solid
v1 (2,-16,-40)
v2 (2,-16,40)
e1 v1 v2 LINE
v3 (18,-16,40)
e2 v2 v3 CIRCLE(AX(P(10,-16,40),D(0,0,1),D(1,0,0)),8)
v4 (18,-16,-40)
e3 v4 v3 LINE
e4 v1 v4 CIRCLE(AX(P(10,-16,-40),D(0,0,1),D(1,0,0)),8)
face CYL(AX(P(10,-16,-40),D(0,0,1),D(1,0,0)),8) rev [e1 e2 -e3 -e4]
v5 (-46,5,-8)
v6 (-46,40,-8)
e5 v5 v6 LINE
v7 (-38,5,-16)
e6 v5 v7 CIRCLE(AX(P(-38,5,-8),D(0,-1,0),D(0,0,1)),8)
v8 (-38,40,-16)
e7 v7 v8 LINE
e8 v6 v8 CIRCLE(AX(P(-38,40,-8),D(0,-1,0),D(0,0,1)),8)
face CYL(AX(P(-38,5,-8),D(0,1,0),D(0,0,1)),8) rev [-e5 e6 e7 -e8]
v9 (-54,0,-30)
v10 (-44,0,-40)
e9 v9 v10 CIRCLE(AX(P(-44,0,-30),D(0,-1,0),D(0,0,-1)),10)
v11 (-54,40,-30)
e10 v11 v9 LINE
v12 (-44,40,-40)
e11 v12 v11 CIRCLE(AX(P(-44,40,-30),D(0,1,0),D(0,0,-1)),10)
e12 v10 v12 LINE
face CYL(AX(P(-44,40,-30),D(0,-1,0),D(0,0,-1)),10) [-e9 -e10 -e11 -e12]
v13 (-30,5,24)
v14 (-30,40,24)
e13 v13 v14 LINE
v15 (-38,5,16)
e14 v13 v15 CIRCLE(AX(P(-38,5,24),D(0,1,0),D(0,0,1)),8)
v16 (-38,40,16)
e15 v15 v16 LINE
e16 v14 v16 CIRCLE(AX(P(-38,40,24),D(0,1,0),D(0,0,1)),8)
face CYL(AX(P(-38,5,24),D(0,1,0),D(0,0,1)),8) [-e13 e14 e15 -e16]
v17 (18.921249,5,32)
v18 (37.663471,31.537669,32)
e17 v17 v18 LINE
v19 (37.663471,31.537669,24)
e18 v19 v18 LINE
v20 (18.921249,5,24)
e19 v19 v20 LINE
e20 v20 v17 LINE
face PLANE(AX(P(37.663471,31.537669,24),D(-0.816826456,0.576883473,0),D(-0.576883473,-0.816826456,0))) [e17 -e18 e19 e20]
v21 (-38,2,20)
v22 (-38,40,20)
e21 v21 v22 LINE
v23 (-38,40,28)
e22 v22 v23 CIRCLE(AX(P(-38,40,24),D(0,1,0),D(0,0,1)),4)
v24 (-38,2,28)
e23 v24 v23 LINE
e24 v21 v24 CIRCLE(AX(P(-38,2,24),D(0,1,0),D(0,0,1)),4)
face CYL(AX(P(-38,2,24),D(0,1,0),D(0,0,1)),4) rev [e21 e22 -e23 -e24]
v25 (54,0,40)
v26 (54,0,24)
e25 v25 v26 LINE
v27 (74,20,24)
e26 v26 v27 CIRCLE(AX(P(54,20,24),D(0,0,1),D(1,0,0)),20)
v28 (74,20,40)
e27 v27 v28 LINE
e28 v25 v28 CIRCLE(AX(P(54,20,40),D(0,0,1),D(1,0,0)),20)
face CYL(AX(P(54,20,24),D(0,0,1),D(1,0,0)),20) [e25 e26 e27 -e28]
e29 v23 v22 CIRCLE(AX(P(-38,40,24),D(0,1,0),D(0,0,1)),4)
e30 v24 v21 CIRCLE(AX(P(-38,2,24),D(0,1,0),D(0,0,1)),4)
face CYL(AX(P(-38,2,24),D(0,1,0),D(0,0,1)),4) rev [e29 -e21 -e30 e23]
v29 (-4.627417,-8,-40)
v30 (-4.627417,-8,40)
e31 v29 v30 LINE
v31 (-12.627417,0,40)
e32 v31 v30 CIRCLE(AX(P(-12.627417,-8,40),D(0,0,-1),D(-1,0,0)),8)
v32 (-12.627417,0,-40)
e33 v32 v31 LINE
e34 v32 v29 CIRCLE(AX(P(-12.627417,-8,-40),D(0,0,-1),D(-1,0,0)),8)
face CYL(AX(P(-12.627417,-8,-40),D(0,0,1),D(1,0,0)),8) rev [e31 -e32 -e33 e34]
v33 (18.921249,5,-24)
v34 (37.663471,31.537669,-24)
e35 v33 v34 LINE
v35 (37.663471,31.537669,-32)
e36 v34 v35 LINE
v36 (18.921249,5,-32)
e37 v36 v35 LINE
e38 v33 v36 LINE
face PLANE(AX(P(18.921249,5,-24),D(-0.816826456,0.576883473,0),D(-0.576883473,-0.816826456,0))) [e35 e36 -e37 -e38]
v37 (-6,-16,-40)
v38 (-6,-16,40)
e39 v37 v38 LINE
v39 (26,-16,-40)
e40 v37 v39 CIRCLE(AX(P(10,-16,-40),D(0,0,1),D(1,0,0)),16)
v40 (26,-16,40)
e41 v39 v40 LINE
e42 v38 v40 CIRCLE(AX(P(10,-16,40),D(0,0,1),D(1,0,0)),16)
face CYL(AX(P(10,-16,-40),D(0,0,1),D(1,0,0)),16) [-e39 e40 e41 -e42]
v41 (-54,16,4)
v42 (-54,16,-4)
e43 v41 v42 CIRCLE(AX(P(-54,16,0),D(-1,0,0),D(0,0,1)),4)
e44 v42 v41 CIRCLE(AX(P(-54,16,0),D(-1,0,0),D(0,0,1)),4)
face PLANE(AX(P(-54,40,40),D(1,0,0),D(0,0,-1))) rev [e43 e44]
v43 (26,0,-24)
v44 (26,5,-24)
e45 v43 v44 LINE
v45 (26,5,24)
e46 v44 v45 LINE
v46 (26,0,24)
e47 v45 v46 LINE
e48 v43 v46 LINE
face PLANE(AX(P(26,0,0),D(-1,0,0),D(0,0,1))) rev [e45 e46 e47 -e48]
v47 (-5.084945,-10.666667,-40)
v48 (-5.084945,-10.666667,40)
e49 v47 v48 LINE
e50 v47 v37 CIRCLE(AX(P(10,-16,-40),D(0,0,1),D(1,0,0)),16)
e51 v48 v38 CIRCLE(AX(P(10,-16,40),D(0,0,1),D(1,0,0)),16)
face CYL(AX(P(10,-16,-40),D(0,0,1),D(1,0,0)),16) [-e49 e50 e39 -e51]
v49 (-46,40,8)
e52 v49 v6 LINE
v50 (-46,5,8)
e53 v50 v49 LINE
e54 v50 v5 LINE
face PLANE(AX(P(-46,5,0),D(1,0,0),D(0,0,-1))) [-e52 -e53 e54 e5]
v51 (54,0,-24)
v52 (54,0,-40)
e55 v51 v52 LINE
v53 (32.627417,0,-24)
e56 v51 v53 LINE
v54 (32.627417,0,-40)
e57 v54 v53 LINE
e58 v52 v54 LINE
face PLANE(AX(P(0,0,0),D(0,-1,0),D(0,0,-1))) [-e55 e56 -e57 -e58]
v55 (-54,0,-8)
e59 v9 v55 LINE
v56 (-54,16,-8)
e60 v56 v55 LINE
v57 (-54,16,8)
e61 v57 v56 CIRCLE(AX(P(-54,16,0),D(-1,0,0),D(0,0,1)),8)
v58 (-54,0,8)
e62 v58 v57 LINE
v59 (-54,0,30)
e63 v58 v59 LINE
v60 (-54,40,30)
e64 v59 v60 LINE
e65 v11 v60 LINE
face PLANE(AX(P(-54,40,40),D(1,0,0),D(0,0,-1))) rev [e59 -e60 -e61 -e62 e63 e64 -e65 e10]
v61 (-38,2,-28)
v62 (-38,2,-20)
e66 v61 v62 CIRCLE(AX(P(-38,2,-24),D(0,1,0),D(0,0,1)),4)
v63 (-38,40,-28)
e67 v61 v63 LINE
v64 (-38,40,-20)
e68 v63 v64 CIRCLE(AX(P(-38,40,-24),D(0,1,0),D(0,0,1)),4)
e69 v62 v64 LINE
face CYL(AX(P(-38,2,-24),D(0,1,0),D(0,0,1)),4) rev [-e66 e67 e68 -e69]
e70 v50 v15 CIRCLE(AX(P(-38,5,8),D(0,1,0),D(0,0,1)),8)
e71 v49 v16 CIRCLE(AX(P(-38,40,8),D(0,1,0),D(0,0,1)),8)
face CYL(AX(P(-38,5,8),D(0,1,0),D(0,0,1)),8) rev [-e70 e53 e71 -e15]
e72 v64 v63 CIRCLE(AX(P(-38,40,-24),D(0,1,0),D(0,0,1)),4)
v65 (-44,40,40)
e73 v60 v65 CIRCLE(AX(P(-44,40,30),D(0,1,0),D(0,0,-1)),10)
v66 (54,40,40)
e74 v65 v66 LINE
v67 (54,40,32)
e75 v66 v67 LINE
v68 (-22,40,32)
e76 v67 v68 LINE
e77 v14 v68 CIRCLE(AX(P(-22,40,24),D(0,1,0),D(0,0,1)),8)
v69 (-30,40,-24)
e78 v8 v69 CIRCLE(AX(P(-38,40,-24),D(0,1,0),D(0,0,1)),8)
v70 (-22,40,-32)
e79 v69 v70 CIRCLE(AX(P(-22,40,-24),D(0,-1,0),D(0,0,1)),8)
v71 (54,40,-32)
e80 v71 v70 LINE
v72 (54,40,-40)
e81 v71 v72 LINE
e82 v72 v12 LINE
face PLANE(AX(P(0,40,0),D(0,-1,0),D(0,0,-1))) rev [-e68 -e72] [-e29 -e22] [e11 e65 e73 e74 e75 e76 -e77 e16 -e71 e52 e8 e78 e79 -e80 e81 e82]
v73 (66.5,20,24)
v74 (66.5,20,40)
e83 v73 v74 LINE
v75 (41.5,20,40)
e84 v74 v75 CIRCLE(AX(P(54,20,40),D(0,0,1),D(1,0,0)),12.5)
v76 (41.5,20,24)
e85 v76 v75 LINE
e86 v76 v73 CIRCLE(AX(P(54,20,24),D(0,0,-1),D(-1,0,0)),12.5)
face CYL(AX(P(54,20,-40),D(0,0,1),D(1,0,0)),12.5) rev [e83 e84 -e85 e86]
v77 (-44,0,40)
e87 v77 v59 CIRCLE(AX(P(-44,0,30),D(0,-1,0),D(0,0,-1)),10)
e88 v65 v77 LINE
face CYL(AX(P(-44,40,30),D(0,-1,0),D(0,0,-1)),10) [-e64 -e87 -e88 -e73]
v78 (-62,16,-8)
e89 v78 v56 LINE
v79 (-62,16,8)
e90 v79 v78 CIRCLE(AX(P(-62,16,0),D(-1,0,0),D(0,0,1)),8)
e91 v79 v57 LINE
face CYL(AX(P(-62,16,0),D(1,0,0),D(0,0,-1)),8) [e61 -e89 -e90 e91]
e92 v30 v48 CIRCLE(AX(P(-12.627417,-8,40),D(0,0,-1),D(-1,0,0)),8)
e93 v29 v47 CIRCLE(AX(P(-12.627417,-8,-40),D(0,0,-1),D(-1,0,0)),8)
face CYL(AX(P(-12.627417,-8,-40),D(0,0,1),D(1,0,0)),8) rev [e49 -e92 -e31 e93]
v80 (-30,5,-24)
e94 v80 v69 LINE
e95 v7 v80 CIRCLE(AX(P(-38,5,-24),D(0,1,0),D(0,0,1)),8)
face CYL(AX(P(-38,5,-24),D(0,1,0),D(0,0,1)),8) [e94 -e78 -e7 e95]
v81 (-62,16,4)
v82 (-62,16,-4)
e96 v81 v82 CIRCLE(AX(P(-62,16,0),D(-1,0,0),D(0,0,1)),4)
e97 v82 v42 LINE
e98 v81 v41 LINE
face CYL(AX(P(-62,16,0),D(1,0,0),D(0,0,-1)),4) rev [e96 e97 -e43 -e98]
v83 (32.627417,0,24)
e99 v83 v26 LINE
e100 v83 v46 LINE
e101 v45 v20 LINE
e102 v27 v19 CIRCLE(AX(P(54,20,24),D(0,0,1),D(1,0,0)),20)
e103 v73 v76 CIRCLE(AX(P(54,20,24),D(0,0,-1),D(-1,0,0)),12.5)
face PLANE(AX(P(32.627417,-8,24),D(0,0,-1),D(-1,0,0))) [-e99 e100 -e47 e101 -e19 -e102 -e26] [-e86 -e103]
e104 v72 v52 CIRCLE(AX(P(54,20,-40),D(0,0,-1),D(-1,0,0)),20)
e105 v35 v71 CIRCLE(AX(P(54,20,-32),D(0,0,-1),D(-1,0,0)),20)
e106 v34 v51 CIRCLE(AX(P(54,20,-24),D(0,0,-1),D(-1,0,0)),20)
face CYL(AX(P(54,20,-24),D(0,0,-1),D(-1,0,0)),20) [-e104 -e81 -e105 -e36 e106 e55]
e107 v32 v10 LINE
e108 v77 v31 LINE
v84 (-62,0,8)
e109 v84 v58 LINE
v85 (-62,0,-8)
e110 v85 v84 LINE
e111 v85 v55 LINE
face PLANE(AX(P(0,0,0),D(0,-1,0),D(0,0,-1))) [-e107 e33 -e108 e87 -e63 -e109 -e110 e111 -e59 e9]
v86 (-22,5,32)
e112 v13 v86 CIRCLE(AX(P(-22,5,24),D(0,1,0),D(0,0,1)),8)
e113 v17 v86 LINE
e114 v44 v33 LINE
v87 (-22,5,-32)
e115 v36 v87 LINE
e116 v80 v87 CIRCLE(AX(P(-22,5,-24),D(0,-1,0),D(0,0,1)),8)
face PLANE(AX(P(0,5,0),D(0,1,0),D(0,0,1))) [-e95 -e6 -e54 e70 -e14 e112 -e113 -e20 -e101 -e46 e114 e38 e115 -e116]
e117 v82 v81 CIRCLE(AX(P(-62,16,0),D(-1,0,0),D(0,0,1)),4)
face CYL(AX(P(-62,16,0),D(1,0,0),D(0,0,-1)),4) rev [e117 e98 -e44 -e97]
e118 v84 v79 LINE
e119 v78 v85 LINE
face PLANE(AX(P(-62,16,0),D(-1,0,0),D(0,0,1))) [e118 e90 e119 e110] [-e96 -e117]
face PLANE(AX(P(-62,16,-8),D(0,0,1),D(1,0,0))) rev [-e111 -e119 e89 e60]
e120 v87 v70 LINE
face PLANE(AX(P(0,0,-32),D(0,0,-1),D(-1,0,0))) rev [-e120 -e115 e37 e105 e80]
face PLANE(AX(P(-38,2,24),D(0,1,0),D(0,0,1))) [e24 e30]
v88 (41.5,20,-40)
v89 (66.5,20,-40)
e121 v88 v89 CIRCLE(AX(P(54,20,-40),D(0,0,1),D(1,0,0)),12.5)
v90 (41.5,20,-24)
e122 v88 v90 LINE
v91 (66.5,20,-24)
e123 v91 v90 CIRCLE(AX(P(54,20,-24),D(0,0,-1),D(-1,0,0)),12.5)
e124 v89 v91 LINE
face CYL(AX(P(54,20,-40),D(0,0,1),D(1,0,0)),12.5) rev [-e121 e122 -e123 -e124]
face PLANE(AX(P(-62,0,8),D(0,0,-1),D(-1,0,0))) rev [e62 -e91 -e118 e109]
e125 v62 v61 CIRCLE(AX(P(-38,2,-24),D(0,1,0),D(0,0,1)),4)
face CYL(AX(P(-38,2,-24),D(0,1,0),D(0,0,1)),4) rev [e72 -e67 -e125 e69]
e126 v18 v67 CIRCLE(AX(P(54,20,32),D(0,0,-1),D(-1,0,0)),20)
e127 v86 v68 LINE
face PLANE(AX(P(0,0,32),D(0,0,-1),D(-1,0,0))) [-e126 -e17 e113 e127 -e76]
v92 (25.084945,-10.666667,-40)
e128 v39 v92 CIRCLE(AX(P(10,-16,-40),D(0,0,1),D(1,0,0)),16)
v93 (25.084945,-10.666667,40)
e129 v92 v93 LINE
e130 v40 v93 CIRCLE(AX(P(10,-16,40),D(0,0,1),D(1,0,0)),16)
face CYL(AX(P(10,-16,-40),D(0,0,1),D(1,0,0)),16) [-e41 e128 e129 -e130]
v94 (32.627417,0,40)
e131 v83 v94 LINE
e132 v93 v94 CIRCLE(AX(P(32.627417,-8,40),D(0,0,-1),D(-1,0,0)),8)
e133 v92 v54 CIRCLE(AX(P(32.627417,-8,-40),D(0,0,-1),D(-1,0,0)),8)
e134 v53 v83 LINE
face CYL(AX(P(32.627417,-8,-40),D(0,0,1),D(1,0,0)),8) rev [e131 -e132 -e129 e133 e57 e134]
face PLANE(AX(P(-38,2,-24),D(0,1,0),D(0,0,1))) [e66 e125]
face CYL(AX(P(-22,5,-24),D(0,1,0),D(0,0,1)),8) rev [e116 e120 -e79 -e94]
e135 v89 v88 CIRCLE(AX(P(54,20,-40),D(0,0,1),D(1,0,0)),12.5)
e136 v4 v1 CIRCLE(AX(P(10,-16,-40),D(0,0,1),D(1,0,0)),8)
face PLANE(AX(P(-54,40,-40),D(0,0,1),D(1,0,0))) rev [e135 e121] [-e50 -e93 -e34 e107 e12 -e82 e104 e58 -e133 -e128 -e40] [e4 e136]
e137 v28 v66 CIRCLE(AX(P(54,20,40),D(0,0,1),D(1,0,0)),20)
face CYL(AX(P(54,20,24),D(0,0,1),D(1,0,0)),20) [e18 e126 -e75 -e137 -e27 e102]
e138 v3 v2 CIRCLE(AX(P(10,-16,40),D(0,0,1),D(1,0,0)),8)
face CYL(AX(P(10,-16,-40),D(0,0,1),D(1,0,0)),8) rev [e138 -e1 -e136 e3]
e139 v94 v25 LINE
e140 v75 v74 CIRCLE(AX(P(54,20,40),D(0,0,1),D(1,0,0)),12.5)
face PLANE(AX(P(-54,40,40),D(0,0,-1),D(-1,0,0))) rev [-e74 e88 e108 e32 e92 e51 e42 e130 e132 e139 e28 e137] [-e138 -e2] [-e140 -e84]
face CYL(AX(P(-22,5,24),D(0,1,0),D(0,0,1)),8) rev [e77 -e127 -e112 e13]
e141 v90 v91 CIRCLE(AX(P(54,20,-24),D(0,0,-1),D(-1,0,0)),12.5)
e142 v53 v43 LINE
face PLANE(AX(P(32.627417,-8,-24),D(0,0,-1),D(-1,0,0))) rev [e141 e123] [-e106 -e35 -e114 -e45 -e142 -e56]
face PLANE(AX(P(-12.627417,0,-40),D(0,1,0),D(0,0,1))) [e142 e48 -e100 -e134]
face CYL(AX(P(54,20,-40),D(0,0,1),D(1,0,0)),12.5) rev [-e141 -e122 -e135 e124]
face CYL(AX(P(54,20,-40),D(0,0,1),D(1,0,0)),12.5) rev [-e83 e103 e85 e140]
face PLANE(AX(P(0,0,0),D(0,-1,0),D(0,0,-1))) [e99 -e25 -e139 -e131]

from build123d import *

# Parameters (mm, degrees)
BASE_BLOCK_SKETCH_W         = 108
BASE_BLOCK_SKETCH_H         = 80
BASE_BLOCK_108X80X40_DEPTH  = 40
BOX_POCKET_SKETCH_W         = 28
BOX_POCKET_SKETCH_H         = 32
THROUGH_CUT_40_DEPTH        = 40
BOX_POCKET_35_DEEP_DEPTH    = 35
FORK_LUGS_DEPTH             = 80
LUG_WEB_16_DEPTH            = 16
POCKET_START                = -16
POCKET_INFILL_BOSS_16_DEPTH = 16
PIN_BORE_SKETCH_R           = 12.5
PIN_BORE_SKETCH_R_2         = 8
PIN_BORES_16_DEPTH          = 117.086174887
TOP_HOLES_SKETCH_R          = 4
TOP_HOLES_8_DEPTH           = 38
BASE_CORNER_FILLETS_R10_R   = 10
LOWER_LUG_SKETCH_R          = 4
LOWER_LUG_BOSS_8_DEPTH      = 8


with BuildPart() as part:
    # Base Block Sketch → Base Block 108x80x40 (new body)
    with BuildSketch(Plane(origin=(0, 0, 0), x_dir=(1, 0, 0), z_dir=(0, 1, 0))):
        Rectangle(BASE_BLOCK_SKETCH_W, BASE_BLOCK_SKETCH_H)
    extrude(amount=BASE_BLOCK_108X80X40_DEPTH)

    # Box Pocket Sketch → Through Cut 40 (cut)
    with BuildSketch(Plane(origin=(0, 40, 0), x_dir=(1, 0, 0), z_dir=(0, 1, 0))):
        with Locations((40, -16)):
            Rectangle(BOX_POCKET_SKETCH_W, BOX_POCKET_SKETCH_H)
        with Locations((40, 16)):
            Rectangle(BOX_POCKET_SKETCH_W, BOX_POCKET_SKETCH_H)
    extrude(amount=-THROUGH_CUT_40_DEPTH, mode=Mode.SUBTRACT)

    # Sketch3_3 → Box Pocket 35 Deep (cut)
    with BuildSketch(Plane(origin=(0, 40, 0), x_dir=(1, 0, 0), z_dir=(0, 1, 0))):
        with BuildLine():
            Line((-22, -32), (26, -32))
            Line((26, -32), (26, 32))
            Line((26, 32), (-22, 32))
            ThreePointArc((-22, 32), (-27.656854249, 29.656854249), (-30, 24))
            ThreePointArc((-30, 24), (-32.343145751, 18.343145751), (-38, 16))
            ThreePointArc((-38, 16), (-43.656854249, 13.656854249), (-46, 8))
            Line((-46, 8), (-46, -8))
            ThreePointArc((-46, -8), (-43.656854249, -13.656854249), (-38, -16))
            ThreePointArc((-38, -16), (-32.343145751, -18.343145751), (-30, -24))
            ThreePointArc((-30, -24), (-27.656854249, -29.656854249), (-22, -32))
        make_face()
    extrude(amount=-BOX_POCKET_35_DEEP_DEPTH, mode=Mode.SUBTRACT)

    # Fork Lug Sketch → Fork Lugs (add)
    with BuildSketch(Plane.XY.offset(40)):
        with BuildLine():
            Line((-12.627416998, 0), (32.627416998, 0))
            ThreePointArc((32.627416998, 0), (26.095444351, -3.381197846), (25.084944665, -10.666666667))
            ThreePointArc((25.084944665, -10.666666667), (10, -32), (-5.084944665, -10.666666667))
            ThreePointArc((-5.084944665, -10.666666667), (-6.095444351, -3.381197846), (-12.627416998, 0))
        make_face()
    extrude(amount=-FORK_LUGS_DEPTH)

    # Lug Web Sketch → Lug Web 16 (add)
    with BuildSketch(Plane.XY.offset(40)):
        with BuildLine():
            Line((37.663470885, 31.537669456), (15.39, 0))
            Line((15.39, 0), (26, 0))
            Line((26, 0), (26.095444351, -3.381197846))
            ThreePointArc((26.095444351, -3.381197846), (28.949810251, -0.895409328), (32.627416998, 0))
            Line((32.627416998, 0), (54, 0))
            ThreePointArc((54, 0), (71.758848346, 29.199092642), (37.663470885, 31.537669456))
        make_face()
    extrude(amount=-LUG_WEB_16_DEPTH)

    # Pocket Infill Sketch → Pocket Infill Boss 16 (add)
    with BuildSketch(Plane(origin=(0, 0, -40), x_dir=(-1, 0, 0), z_dir=(0, 0, -1)).offset(POCKET_START)):
        with BuildLine():
            Line((-32.627416998, 0), (-54, 0))
            ThreePointArc((-54, 0), (-74, 20), (-54, 40))
            ThreePointArc((-54, 40), (-44.800907358, 37.758848346), (-37.663470885, 31.537669456))
            Line((-37.663470885, 31.537669456), (-18.921248705, 5))
            Line((-18.921248705, 5), (-26, 5))
            Line((-26, 5), (-26, -3.519225074))
            ThreePointArc((-26, -3.519225074), (-28.87549745, -0.934371953), (-32.627416998, 0))
        make_face()
    extrude(amount=POCKET_INFILL_BOSS_16_DEPTH)

    # Pin Bore Sketch → Pin Bores _16 (cut, through all)
    with BuildSketch(Plane.XY.offset(40)):
        with Locations((54, 20)):
            Circle(PIN_BORE_SKETCH_R)
        with Locations((10, -16)):
            Circle(PIN_BORE_SKETCH_R_2)
    extrude(amount=-PIN_BORES_16_DEPTH, mode=Mode.SUBTRACT)

    # Top Holes Sketch → Top Holes _8 (cut)
    with BuildSketch(Plane(origin=(0, 40, 0), x_dir=(1, 0, 0), z_dir=(0, 1, 0))):
        with Locations(Location((-38, 24, 0), (0, 0, 270))):
            Circle(TOP_HOLES_SKETCH_R)
        with Locations(Location((-38, -24, 0), (0, 0, 270))):
            Circle(TOP_HOLES_SKETCH_R)
    extrude(amount=-TOP_HOLES_8_DEPTH, mode=Mode.SUBTRACT)

    # Base Corner Fillets R10
    base_corner_fillets_r10_edges = [part.edges().sort_by_distance(p)[0] for p in [
        (-54, 20, 40),
        (-54, 20, -40),
    ]]
    fillet(base_corner_fillets_r10_edges, radius=BASE_CORNER_FILLETS_R10_R)

    # Lower Lug Sketch → Lower Lug Boss 8 (add)
    with BuildSketch(Plane.ZY.offset(54)):
        with BuildLine():
            Line((-8, 16), (-8, 0))
            Line((-8, 0), (8, 0))
            Line((8, 0), (8, 16))
            ThreePointArc((8, 16), (0, 24), (-8, 16))
        make_face()
        with Locations((0, 16)):
            Circle(LOWER_LUG_SKETCH_R, mode=Mode.SUBTRACT)
    extrude(amount=LOWER_LUG_BOSS_8_DEPTH)


solid = part.part
